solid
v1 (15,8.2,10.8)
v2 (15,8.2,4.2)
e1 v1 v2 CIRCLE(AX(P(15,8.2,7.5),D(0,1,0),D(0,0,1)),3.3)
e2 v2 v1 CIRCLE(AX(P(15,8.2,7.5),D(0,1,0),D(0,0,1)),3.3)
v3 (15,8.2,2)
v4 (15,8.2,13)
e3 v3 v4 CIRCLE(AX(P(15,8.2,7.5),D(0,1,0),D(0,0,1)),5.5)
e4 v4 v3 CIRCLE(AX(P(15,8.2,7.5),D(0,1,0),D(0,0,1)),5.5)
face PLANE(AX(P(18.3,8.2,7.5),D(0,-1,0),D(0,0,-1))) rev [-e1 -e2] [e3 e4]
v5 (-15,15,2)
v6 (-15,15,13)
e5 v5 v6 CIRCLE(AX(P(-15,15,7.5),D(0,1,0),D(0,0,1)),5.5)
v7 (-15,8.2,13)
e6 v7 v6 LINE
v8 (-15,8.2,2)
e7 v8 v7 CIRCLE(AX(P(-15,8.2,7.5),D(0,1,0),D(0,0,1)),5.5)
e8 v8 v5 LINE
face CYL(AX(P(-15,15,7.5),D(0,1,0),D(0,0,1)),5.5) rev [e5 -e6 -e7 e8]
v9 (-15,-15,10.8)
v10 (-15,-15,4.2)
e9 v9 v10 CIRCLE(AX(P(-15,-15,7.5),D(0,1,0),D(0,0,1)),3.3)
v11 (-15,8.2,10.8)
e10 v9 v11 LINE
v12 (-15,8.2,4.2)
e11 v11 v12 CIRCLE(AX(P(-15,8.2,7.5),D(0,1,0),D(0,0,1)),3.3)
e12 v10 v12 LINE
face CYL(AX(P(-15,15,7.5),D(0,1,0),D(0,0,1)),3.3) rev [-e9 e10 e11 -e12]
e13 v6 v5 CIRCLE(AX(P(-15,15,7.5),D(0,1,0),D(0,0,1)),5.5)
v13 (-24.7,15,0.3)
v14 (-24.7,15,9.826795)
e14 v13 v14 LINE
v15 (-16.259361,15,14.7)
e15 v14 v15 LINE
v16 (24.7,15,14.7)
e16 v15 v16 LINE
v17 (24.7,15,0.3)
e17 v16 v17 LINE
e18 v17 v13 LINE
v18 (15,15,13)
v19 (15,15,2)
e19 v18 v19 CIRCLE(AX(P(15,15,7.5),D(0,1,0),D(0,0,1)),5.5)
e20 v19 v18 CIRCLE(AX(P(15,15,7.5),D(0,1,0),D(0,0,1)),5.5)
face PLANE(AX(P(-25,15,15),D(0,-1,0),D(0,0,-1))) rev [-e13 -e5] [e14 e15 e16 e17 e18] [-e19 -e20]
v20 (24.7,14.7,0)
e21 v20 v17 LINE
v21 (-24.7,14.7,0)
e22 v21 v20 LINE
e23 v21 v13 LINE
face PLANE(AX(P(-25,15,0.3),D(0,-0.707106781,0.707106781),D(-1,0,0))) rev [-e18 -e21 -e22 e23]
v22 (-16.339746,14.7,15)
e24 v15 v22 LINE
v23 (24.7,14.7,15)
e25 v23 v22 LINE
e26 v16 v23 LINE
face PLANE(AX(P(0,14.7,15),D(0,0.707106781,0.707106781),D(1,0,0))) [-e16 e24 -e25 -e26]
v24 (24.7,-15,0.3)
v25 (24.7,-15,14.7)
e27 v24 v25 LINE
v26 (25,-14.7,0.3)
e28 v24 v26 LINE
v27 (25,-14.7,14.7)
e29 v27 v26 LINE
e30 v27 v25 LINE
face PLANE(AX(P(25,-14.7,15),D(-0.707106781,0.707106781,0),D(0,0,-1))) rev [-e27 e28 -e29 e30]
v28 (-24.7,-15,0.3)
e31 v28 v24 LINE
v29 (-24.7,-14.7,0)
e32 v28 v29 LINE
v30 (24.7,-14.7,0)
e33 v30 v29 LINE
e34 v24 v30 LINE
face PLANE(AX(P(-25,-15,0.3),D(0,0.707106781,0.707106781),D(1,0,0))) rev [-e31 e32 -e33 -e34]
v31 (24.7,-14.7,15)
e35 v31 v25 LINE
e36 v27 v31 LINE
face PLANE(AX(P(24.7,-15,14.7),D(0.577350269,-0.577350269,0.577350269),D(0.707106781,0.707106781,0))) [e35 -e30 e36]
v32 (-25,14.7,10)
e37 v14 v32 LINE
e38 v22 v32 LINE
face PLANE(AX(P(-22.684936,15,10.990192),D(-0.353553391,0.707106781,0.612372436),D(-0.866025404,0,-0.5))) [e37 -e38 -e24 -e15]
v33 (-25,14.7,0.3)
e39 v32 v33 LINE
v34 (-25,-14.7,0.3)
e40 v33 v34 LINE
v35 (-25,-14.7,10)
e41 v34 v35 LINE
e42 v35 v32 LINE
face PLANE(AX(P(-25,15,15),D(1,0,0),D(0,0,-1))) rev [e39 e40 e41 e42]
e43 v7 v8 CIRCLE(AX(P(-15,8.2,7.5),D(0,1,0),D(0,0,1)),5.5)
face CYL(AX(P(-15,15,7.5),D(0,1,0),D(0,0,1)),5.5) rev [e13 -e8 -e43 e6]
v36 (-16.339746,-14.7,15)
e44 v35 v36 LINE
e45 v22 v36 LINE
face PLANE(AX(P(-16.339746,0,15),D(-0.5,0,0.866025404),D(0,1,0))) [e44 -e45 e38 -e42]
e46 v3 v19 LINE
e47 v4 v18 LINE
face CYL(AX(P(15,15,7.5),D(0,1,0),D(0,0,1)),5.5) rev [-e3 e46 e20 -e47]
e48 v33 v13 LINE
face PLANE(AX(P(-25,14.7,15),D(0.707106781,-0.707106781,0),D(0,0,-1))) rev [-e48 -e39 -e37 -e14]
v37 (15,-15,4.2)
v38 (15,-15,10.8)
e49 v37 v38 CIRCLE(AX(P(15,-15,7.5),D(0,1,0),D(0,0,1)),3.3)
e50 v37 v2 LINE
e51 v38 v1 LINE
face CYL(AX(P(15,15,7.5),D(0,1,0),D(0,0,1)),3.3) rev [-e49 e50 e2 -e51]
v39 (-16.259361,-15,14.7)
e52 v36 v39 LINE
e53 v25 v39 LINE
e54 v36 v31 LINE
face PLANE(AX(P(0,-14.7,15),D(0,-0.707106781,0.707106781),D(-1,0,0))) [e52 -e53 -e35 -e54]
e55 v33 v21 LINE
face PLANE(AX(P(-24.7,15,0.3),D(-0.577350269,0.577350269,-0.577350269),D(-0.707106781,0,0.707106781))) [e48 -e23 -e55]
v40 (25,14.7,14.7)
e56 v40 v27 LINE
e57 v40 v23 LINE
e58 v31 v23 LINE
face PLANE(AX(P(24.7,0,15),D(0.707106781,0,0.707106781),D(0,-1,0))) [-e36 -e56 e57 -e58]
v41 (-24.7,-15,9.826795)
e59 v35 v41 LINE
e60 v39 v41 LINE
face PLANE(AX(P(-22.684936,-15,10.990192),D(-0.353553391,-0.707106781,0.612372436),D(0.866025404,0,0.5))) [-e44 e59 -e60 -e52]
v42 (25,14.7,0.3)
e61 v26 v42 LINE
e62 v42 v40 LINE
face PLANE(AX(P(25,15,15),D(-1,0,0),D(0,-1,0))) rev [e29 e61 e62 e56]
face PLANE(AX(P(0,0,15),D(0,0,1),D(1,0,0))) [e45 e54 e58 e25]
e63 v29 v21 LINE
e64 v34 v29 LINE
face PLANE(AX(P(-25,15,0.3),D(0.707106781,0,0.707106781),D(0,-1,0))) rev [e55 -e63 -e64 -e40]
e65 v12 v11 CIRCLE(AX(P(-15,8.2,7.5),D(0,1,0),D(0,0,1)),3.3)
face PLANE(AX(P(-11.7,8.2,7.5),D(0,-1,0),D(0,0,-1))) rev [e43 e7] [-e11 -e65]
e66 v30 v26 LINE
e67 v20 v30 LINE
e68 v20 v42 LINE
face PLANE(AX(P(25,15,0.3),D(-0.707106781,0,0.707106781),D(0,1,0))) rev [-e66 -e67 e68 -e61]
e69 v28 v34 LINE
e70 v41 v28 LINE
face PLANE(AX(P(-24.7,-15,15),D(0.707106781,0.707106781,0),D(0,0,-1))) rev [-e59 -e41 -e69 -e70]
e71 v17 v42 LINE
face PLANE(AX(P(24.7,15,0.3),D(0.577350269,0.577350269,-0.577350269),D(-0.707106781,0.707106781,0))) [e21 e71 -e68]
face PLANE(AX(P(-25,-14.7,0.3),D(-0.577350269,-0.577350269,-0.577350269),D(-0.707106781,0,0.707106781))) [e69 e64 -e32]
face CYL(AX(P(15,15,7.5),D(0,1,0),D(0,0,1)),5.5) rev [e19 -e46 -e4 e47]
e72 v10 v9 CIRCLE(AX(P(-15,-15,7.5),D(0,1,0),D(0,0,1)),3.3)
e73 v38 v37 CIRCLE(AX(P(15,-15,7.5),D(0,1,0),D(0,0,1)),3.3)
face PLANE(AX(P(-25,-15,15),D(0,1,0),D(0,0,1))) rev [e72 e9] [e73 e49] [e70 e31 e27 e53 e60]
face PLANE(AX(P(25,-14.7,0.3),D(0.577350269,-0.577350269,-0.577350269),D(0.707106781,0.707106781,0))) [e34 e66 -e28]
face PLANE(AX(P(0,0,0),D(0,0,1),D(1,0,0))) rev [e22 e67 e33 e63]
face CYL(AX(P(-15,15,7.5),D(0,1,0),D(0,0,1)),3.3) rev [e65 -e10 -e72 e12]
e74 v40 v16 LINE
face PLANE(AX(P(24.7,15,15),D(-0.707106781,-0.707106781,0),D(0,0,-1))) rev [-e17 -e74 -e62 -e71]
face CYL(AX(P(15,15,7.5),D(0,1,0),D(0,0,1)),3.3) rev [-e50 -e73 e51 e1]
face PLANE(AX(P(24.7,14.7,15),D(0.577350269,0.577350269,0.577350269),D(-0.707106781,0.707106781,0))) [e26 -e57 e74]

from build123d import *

# Parameters (mm, degrees)
SKETCH_1_W                = 50
SKETCH_1_H                = 30
EXTRUDE_1_DEPTH           = 15
HOLE_WIZARD_1_D           = 6.6
HOLE_WIZARD_1_CBORE_D     = 11
HOLE_WIZARD_1_CBORE_DEPTH = 6.8
CHAMFER_1_SIZE            = 5
CHAMFER_1_SIZE2           = 8.660254038
CHAMFER_2_SIZE            = 0.3


with BuildPart() as part:
    # 草图1 → 凸台-拉伸1 (new body)
    with BuildSketch(Plane.XY):
        Rectangle(SKETCH_1_W, SKETCH_1_H)
    extrude(amount=EXTRUDE_1_DEPTH)

    # 打孔尺寸根据内六角圆柱头螺钉的类型1 (through all)
    with Locations(Plane(origin=(0, 15, 0), x_dir=(1, 0, 0), z_dir=(0, 1, 0))):
        with Locations((-15, -7.5), (15, -7.5)):
            CounterBoreHole(HOLE_WIZARD_1_D / 2, HOLE_WIZARD_1_CBORE_D / 2, HOLE_WIZARD_1_CBORE_DEPTH)

    # 倒角1
    chamfer_1_edges = [part.edges().sort_by_distance(p)[0] for p in [
        (-25, 0, 15),
    ]]
    chamfer_1_side = [part.faces().sort_by_distance(p)[0] for p in [
        (-25, 0, 7.5),
    ]]
    chamfer(chamfer_1_edges, length=CHAMFER_1_SIZE, length2=CHAMFER_1_SIZE2, reference=chamfer_1_side[0])

    # 倒角2
    chamfer_2_edges = [part.edges().sort_by_distance(p)[0] for p in [
        (4.330127019, -15, 15),
        (-25, -15, 5),
        (-20.669872981, -15, 12.5),
        (-25, 15, 5),
        (-20.669872981, 15, 12.5),
        (25, 0, 15),
        (0, -15, 0),
        (-25, 0, 0),
        (0, 15, 0),
        (25, 0, 0),
        (4.330127019, 15, 15),
        (25, -15, 7.5),
        (25, 15, 7.5),
    ]]
    chamfer(chamfer_2_edges, length=CHAMFER_2_SIZE)


solid = part.part
